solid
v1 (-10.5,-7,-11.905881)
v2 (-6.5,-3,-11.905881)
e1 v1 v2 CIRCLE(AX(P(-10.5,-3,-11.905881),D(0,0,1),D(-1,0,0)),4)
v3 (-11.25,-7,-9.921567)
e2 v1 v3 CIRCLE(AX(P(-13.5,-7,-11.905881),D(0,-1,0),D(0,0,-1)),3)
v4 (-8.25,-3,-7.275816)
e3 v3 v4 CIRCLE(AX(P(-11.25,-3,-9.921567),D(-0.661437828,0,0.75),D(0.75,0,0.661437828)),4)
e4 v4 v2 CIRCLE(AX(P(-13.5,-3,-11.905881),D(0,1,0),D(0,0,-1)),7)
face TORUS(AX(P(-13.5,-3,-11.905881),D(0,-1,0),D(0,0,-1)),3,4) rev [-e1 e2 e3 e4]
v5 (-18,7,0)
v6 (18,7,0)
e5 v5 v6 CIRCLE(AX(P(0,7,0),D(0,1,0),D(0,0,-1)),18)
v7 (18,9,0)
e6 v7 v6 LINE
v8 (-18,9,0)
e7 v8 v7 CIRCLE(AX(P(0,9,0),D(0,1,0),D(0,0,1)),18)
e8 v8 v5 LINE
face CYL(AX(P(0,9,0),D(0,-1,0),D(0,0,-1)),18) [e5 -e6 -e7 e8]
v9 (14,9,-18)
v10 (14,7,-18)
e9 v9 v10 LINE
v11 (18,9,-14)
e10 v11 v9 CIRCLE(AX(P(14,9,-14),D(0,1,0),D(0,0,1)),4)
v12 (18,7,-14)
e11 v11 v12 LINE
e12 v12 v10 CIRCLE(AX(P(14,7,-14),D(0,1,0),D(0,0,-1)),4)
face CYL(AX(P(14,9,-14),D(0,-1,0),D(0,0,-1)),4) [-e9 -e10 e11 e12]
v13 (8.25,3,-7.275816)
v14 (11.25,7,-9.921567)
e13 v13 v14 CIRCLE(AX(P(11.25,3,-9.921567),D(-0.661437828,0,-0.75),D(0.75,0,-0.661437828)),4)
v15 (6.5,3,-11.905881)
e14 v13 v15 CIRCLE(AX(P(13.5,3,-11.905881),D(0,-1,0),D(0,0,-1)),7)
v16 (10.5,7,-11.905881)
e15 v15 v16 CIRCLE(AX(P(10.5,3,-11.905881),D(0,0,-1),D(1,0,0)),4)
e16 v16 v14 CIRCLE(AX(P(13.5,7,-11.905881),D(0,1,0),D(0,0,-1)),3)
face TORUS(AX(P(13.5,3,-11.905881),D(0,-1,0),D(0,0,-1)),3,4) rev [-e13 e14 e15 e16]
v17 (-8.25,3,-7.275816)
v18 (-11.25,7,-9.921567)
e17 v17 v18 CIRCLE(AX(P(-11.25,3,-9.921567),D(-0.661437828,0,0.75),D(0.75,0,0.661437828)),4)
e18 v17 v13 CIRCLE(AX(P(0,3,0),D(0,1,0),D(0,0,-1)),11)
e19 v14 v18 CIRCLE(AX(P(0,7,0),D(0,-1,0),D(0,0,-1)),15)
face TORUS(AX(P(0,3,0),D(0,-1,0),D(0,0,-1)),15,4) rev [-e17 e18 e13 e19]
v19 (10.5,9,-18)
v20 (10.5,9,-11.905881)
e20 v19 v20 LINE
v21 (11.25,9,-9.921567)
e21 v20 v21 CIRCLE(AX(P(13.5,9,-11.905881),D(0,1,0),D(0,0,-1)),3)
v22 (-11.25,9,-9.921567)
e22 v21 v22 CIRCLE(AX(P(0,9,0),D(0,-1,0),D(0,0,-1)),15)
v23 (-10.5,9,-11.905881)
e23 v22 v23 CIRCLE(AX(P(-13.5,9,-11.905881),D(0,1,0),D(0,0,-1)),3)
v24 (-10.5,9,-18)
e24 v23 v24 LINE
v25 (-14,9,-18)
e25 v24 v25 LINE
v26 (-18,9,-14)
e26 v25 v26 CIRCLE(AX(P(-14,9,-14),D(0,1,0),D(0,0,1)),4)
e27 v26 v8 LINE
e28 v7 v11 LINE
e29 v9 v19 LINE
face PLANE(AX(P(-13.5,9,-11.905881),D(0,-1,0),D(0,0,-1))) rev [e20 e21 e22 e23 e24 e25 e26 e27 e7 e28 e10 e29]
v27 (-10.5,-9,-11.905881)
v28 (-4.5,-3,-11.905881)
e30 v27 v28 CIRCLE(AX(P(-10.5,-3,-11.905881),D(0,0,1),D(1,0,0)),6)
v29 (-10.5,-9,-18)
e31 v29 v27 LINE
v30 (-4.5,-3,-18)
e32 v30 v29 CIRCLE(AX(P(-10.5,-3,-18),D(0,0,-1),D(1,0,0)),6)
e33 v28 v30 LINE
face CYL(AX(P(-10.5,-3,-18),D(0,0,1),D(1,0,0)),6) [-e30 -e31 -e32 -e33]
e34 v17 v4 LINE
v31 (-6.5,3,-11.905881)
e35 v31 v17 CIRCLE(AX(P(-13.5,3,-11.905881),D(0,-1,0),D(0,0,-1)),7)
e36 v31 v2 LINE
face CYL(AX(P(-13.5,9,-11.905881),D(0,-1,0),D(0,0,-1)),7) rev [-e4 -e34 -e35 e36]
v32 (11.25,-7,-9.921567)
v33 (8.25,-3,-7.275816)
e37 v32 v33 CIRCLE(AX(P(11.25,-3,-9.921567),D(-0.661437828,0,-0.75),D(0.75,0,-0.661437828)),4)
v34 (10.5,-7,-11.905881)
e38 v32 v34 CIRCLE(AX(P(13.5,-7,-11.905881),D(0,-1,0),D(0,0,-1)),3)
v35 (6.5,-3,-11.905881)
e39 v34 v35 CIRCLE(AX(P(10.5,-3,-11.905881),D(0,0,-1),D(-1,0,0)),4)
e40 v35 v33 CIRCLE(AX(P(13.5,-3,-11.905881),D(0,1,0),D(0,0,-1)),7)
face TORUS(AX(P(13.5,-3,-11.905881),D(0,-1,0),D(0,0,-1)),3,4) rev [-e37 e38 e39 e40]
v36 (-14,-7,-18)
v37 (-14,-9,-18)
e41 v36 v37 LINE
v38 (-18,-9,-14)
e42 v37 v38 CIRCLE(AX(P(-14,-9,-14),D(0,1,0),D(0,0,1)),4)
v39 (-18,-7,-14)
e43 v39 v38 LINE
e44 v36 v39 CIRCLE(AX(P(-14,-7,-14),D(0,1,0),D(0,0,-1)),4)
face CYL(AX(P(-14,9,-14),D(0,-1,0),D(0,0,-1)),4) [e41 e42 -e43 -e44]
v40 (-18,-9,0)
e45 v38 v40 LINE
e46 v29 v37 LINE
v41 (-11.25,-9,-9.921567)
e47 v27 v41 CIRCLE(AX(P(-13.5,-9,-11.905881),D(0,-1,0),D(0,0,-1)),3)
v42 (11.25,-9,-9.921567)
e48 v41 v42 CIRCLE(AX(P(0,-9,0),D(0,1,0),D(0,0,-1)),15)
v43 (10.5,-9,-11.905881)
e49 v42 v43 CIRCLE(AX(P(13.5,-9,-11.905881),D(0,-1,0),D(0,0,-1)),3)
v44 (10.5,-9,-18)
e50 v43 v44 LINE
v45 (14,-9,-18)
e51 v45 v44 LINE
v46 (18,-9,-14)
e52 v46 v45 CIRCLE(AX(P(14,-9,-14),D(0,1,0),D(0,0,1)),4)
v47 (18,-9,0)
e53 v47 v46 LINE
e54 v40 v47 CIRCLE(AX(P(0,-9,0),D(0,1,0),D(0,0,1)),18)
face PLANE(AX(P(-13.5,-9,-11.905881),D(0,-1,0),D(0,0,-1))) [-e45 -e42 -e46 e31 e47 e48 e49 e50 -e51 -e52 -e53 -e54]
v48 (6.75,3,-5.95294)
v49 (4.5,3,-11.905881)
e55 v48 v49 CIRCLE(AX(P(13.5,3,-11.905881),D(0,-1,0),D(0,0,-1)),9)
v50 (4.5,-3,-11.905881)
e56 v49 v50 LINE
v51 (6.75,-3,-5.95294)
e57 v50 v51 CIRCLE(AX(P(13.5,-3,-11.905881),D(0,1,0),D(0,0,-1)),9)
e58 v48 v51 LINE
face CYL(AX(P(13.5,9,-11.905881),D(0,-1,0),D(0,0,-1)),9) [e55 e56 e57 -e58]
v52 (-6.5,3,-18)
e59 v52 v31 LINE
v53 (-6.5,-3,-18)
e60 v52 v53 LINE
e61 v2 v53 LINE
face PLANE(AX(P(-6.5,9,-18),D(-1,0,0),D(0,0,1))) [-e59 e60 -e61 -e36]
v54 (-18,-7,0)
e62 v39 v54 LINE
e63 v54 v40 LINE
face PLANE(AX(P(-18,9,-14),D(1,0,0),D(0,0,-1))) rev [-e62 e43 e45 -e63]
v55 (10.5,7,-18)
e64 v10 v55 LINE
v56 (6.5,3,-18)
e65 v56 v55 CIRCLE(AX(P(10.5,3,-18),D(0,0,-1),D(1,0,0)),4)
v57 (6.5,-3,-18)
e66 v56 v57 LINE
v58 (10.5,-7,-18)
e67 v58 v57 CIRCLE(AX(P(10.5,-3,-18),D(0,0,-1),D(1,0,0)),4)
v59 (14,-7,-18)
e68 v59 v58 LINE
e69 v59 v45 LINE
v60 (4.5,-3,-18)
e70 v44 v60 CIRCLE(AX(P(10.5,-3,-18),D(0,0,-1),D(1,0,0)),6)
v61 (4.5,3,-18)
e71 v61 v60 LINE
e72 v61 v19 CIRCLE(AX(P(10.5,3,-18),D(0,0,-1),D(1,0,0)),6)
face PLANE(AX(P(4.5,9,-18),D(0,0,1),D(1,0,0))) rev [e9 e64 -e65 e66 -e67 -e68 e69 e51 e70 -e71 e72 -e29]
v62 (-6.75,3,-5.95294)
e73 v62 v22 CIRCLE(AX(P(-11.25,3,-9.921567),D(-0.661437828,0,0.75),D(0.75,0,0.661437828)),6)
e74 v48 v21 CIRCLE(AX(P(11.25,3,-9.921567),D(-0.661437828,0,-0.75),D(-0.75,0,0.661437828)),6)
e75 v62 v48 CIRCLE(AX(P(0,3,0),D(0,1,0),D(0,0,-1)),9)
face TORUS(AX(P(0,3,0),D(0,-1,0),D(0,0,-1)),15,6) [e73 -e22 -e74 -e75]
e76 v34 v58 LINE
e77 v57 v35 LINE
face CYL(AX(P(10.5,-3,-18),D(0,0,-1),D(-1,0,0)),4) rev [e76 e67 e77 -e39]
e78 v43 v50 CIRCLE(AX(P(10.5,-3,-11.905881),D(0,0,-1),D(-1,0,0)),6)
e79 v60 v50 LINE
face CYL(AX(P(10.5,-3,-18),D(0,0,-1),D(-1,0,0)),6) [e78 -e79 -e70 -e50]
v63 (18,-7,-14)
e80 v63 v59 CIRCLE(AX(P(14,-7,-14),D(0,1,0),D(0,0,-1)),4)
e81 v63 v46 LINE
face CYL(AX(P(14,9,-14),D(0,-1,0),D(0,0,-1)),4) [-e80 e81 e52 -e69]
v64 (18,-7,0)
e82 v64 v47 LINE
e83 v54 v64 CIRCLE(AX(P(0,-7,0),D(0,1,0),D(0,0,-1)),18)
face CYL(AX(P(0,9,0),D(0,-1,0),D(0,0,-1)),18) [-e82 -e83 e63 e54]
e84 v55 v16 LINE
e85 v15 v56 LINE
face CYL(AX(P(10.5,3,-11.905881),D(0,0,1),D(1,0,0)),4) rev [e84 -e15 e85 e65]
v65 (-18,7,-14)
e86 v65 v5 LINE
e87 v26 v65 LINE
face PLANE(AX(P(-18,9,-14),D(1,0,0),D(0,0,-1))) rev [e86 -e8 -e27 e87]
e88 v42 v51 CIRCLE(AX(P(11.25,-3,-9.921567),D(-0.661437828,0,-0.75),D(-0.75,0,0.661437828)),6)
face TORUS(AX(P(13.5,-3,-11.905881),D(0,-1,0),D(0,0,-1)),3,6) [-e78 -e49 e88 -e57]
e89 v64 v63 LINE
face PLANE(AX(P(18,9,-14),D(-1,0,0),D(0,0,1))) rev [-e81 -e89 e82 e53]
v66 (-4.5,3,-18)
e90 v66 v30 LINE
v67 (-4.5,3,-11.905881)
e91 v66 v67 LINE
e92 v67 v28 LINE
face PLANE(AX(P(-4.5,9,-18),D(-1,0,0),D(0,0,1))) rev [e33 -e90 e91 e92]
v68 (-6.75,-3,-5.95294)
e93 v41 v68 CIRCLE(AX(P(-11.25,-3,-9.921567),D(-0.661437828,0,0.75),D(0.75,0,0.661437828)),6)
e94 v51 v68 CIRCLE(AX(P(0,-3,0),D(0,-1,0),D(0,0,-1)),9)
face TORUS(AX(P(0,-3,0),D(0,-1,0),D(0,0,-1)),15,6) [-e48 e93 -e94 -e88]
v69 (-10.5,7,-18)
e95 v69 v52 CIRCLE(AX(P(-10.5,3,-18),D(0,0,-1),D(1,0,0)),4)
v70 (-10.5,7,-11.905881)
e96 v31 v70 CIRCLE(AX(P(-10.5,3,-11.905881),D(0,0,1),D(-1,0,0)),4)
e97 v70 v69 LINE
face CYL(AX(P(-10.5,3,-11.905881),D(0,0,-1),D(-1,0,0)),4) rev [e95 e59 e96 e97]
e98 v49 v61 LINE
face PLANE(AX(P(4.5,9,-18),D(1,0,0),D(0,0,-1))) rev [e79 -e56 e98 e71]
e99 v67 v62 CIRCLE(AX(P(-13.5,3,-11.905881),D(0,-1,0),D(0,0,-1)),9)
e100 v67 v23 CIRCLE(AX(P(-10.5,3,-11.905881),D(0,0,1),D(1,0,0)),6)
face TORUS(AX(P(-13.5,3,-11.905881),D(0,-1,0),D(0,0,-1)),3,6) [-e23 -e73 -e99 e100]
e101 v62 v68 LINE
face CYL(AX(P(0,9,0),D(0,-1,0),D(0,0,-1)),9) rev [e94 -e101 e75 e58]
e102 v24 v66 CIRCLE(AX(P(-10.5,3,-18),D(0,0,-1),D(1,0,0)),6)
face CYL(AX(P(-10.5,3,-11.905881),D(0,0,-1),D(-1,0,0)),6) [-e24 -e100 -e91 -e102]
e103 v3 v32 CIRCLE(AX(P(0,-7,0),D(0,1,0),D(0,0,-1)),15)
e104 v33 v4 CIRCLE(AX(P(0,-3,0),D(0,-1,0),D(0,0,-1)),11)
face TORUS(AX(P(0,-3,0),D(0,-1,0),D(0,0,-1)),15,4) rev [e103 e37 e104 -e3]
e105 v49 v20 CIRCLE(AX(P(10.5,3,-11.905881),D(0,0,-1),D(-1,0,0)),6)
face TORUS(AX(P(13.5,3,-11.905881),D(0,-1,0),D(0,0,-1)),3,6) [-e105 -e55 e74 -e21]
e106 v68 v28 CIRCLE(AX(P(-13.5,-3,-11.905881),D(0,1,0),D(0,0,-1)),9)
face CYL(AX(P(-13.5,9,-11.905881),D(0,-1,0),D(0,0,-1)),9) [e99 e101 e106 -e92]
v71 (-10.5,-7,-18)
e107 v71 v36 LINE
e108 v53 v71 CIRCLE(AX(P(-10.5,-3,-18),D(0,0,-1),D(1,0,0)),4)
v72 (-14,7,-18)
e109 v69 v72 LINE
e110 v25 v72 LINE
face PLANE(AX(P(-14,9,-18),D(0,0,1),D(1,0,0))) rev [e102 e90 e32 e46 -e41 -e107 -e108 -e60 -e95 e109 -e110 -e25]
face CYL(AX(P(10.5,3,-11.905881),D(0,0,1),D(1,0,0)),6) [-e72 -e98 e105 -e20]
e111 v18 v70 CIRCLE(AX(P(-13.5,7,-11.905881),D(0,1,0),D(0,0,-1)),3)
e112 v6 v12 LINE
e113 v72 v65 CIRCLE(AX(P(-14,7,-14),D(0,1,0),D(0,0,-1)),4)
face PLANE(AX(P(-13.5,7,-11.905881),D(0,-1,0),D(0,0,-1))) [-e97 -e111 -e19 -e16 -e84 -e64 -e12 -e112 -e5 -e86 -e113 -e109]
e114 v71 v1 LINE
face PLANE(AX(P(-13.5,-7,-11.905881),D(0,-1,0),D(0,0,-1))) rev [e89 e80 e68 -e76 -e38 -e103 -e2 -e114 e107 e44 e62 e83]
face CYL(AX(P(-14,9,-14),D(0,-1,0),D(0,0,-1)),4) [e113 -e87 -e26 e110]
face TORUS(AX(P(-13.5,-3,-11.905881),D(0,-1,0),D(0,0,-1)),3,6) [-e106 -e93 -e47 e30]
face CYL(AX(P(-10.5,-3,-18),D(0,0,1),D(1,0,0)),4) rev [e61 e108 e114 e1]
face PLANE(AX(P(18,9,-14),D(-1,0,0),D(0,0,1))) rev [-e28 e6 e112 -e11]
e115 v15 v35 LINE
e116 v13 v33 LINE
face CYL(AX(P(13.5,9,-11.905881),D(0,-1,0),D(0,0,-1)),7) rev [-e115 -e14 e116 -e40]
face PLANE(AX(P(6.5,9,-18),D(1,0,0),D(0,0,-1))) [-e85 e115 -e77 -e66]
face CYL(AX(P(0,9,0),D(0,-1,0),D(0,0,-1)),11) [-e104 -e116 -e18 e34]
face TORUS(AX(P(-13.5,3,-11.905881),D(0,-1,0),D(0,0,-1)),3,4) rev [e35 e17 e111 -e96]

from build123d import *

# Parameters (mm, degrees)
CLIP_BODY_EXTRUDE_18MM_DEPTH = 9
EDGE_FILLETS_R6_R            = 6
SHELL_WALL_2MM_T             = -2


with BuildPart() as part:
    # Clip Profile Sketch → Clip Body Extrude 18mm (new, symmetric)
    with BuildSketch(Plane(origin=(0, 0, 0), x_dir=(1, 0, 0), z_dir=(0, 1, 0))):
        with BuildLine():
            Line((-14, 18), (-4.5, 18))
            Line((-4.5, 18), (-4.5, 11.9058809))
            ThreePointArc((-4.5, 11.9058809), (-5.08127088, 8.723900384), (-6.75, 5.95294045))
            ThreePointArc((-6.75, 5.95294045), (0, -9), (6.75, 5.95294045))
            ThreePointArc((6.75, 5.95294045), (5.08127088, 8.723900384), (4.5, 11.9058809))
            Line((4.5, 11.9058809), (4.5, 18))
            Line((4.5, 18), (14, 18))
            ThreePointArc((14, 18), (16.828427125, 16.828427125), (18, 14))
            Line((18, 14), (18, 0))
            ThreePointArc((18, 0), (0, -18), (-18, 0))
            Line((-18, 0), (-18, 14))
            ThreePointArc((-18, 14), (-16.828427125, 16.828427125), (-14, 18))
        make_face()
    extrude(amount=CLIP_BODY_EXTRUDE_18MM_DEPTH, both=True)

    # Edge Fillets R6
    edge_fillets_r6_edges = [part.edges().sort_by_distance(p)[0] for p in [
        (0, -9, 9),
        (5.08127088, -9, -8.723900384),
        (4.5, -9, -14.95294045),
        (-4.5, -9, -14.95294045),
        (-5.08127088, -9, -8.723900384),
        (4.5, 9, -14.95294045),
        (5.08127088, 9, -8.723900384),
        (0, 9, 9),
        (-5.08127088, 9, -8.723900384),
        (-4.5, 9, -14.95294045),
    ]]
    fillet(edge_fillets_r6_edges, radius=EDGE_FILLETS_R6_R)

    # Shell Wall 2mm
    shell_wall_2mm_openings = [part.faces().sort_by_distance(p)[0] for p in [
        (-9.588709649, 0, -18),
        (-16.828427125, 0, -16.828427125),
        (-18, 0, -7),
        (0, 0, 18),
        (18, 0, -7),
        (16.828427125, 0, -16.828427125),
        (9.588709649, 0, -18),
    ]]
    offset(amount=SHELL_WALL_2MM_T, openings=shell_wall_2mm_openings, kind=Kind.INTERSECTION)


solid = part.part
